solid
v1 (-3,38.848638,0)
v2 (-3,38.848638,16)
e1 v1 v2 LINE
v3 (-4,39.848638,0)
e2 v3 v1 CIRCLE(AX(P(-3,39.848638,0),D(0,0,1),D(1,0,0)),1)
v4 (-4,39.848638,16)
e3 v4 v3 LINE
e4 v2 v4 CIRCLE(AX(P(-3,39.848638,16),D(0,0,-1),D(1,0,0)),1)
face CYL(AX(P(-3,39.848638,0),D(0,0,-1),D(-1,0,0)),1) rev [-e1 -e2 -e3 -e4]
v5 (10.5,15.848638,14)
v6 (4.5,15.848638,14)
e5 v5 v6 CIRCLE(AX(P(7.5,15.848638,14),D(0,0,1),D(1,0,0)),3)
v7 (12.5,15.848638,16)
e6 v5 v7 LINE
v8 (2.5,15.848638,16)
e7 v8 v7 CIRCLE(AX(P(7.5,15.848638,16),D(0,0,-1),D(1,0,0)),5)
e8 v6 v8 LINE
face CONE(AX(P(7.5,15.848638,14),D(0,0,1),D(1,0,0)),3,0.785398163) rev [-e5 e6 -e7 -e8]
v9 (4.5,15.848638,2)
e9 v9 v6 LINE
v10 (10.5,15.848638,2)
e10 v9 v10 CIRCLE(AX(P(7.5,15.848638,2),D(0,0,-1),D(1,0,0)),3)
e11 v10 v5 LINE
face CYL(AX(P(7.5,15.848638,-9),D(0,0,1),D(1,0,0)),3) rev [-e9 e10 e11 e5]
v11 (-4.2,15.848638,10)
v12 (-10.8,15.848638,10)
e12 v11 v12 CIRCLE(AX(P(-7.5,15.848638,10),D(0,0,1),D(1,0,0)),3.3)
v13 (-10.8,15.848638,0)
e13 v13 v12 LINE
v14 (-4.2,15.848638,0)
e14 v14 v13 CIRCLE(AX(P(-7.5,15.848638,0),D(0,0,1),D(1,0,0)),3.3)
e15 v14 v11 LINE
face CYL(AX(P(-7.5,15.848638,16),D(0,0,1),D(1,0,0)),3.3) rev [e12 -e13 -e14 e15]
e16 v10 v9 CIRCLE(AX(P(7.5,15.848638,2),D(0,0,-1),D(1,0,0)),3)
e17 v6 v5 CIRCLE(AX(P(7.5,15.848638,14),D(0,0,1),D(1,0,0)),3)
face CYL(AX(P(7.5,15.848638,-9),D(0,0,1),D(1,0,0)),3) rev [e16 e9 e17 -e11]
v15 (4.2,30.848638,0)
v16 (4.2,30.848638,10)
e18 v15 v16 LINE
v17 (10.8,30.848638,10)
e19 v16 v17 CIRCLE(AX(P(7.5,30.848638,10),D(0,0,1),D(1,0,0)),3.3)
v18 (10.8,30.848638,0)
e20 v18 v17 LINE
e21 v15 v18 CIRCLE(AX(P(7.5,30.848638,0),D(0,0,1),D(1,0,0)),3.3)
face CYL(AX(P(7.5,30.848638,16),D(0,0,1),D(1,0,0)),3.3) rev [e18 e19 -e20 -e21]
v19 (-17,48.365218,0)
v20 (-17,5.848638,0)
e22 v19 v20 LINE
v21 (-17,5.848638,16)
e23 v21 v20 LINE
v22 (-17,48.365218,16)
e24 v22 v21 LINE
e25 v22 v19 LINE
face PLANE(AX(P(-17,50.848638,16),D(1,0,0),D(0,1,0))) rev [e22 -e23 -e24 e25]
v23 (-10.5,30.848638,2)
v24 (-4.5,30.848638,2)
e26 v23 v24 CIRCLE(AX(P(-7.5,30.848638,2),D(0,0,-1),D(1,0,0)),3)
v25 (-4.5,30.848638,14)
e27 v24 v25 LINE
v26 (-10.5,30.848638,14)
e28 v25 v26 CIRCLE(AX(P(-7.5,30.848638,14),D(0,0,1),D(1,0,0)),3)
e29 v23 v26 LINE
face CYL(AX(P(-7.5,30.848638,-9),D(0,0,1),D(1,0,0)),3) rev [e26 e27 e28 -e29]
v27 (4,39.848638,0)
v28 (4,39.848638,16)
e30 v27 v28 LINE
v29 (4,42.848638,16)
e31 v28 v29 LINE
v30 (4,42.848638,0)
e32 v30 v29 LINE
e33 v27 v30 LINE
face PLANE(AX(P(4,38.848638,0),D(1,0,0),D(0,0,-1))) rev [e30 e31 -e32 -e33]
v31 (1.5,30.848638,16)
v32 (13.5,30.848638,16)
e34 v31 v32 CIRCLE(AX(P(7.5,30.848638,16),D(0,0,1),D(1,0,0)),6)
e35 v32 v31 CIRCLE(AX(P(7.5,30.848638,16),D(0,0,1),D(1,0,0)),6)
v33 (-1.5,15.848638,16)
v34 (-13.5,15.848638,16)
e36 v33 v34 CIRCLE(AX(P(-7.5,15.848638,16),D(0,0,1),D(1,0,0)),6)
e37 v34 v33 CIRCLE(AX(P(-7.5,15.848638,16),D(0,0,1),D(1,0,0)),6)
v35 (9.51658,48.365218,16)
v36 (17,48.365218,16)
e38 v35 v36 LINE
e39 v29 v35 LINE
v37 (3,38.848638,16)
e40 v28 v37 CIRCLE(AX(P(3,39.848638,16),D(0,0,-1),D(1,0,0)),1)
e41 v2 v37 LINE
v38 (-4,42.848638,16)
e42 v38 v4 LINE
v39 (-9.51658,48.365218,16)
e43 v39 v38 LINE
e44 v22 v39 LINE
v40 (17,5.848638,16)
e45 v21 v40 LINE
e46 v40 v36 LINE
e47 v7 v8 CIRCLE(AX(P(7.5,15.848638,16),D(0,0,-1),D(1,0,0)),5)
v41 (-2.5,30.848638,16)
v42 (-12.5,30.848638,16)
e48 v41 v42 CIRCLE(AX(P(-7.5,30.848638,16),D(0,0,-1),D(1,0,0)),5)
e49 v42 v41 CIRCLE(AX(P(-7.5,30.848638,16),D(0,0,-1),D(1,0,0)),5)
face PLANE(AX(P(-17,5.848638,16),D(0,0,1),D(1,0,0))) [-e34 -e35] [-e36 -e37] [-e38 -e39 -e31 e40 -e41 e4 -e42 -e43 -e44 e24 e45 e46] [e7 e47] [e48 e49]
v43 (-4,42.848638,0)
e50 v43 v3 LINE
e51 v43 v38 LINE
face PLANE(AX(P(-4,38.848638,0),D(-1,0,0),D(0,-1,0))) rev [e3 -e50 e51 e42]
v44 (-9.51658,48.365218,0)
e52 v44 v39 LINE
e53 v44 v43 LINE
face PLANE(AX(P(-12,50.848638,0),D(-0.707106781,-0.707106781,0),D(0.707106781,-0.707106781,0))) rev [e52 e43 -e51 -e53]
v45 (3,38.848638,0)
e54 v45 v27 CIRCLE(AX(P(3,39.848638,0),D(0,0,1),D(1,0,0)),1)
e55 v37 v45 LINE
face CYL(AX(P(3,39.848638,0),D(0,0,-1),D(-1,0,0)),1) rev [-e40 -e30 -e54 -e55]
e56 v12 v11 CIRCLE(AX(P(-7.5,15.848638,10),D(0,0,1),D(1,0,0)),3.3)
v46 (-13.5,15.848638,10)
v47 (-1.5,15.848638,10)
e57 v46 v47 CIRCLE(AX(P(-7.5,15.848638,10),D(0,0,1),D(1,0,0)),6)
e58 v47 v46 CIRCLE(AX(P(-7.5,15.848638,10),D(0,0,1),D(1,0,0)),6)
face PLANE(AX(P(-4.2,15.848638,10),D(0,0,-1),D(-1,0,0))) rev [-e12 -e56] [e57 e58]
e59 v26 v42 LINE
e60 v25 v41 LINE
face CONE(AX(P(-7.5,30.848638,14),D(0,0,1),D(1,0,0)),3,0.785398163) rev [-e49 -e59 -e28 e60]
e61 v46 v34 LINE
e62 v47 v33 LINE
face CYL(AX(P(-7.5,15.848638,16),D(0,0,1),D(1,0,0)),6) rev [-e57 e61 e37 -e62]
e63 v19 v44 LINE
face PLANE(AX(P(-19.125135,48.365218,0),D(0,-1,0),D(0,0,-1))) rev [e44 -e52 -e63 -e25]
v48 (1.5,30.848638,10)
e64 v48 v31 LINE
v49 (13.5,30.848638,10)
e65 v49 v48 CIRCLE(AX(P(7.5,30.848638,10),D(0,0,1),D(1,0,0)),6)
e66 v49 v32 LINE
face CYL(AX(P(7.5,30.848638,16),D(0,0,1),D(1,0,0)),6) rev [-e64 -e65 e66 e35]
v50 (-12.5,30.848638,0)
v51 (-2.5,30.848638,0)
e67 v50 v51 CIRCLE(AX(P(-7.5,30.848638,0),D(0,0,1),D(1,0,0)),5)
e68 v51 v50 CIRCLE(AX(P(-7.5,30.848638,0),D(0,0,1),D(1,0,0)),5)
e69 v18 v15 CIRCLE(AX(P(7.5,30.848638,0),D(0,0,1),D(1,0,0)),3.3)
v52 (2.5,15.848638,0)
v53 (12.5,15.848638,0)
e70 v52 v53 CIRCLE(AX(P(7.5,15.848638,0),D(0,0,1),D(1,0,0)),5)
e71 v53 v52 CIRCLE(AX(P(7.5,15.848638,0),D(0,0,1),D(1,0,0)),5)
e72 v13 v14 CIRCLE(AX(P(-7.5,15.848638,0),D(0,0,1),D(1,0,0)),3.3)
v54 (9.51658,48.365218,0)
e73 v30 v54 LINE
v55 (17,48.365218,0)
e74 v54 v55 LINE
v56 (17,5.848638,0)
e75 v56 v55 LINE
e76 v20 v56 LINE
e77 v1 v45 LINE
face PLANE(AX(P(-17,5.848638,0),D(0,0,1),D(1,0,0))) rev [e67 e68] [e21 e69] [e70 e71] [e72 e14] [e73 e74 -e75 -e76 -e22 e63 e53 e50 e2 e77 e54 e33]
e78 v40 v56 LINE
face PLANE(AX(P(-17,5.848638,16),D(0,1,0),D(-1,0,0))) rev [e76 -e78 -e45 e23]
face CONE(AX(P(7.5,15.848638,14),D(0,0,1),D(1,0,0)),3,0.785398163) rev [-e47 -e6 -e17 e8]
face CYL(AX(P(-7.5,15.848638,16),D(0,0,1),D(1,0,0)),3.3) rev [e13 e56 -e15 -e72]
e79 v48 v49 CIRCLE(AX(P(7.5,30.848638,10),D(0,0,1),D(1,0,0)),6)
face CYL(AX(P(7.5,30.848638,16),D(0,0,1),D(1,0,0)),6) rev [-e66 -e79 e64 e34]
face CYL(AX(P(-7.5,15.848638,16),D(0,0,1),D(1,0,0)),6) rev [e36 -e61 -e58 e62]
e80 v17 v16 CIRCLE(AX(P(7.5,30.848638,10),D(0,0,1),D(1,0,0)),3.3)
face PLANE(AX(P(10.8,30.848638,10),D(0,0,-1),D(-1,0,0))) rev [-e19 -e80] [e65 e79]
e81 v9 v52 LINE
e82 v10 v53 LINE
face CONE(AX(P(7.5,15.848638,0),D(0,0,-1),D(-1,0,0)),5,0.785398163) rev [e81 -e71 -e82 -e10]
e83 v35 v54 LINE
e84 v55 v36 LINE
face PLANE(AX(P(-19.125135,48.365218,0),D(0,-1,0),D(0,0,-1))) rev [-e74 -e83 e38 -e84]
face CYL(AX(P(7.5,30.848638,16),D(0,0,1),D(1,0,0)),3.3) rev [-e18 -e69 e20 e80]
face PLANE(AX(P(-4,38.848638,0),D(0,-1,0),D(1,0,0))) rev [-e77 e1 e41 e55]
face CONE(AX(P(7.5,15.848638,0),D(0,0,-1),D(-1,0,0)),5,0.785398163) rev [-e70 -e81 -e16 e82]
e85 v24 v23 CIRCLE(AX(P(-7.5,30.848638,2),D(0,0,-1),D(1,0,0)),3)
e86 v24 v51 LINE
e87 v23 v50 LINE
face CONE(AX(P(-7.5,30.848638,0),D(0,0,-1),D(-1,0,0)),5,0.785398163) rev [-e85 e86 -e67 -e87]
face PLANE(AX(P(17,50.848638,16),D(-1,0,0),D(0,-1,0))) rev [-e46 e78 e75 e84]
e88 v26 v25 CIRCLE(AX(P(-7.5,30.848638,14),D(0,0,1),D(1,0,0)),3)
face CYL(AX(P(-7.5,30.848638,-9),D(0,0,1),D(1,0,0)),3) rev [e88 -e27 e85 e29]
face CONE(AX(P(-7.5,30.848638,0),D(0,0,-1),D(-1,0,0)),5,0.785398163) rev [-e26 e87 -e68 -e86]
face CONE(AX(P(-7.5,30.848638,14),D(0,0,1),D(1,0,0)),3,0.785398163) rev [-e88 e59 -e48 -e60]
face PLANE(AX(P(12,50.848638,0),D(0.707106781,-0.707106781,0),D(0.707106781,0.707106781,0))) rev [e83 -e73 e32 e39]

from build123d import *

# Parameters (mm, degrees)
SKETCH1_W                                = 34
SKETCH1_H                                = 45
BASE_EXTRUDE_DEPTH                       = 16
CUT_EXTRUDE1_DEPTH                       = 56.951622292
CBORE_FOR_M5_HEX_HEAD_SCREW1_D           = 6.6
CBORE_FOR_M5_HEX_HEAD_SCREW1_CBORE_D     = 12
CBORE_FOR_M5_HEX_HEAD_SCREW1_CBORE_DEPTH = 6
SKETCH3_R                                = 3
CUT_EXTRUDE4_DEPTH                       = 25
CHAMFER3_SIZE                            = 2
CHAMFER4_SIZE                            = 2
CBORE_FOR_M5_HEX_HEAD_SCREW2_D           = 6.6
CBORE_FOR_M5_HEX_HEAD_SCREW2_CBORE_D     = 12
CBORE_FOR_M5_HEX_HEAD_SCREW2_CBORE_DEPTH = 6
FILLET1_R                                = 1
FILLET2_R                                = 1
SKETCH13_W                               = 37.795873191
SKETCH13_H                               = 5.669380978
CUT_EXTRUDE5_DEPTH                       = 56.951622292


with BuildPart() as part:
    # Sketch1 → Base-Extrude (new body)
    with BuildSketch(Plane.XY):
        with Locations((0, 28.348638498)):
            Rectangle(SKETCH1_W, SKETCH1_H)
    extrude(amount=BASE_EXTRUDE_DEPTH)

    # Sketch2 → Cut-Extrude1 (cut, through all)
    with BuildSketch(Plane.XY.offset(16)):
        Polygon((-4, 38.848638498), (4, 38.848638498), (4, 42.848638498), (12, 50.848638498), (-12, 50.848638498), (-4, 42.848638498), align=None)
    extrude(amount=-CUT_EXTRUDE1_DEPTH, mode=Mode.SUBTRACT)

    # CBORE for M5 Hex Head Screw1 (through all)
    with Locations(Plane.XY.offset(16)):
        with Locations((7.5, 30.848638498)):
            CounterBoreHole(CBORE_FOR_M5_HEX_HEAD_SCREW1_D / 2, CBORE_FOR_M5_HEX_HEAD_SCREW1_CBORE_D / 2, CBORE_FOR_M5_HEX_HEAD_SCREW1_CBORE_DEPTH)

    # Sketch3 → Cut-Extrude4 (cut)
    with BuildSketch(Plane.XY.offset(16)):
        with Locations((-7.5, 30.848638498)):
            Circle(SKETCH3_R)
        with Locations((7.5, 15.848638498)):
            Circle(SKETCH3_R)
    extrude(amount=-CUT_EXTRUDE4_DEPTH, mode=Mode.SUBTRACT)

    # Chamfer3
    chamfer3_edges = [part.edges().sort_by_distance(p)[0] for p in [
        (-10.5, 30.848638498, 16),
        (4.5, 15.848638498, 16),
    ]]
    chamfer(chamfer3_edges, length=CHAMFER3_SIZE)

    # Chamfer4
    chamfer4_edges = [part.edges().sort_by_distance(p)[0] for p in [
        (-10.5, 30.848638498, 0),
        (4.5, 15.848638498, 0),
    ]]
    chamfer(chamfer4_edges, length=CHAMFER4_SIZE)

    # CBORE for M5 Hex Head Screw2 (through all)
    with Locations(Plane.XY.offset(16)):
        with Locations((-7.5, 15.848638498)):
            CounterBoreHole(CBORE_FOR_M5_HEX_HEAD_SCREW2_D / 2, CBORE_FOR_M5_HEX_HEAD_SCREW2_CBORE_D / 2, CBORE_FOR_M5_HEX_HEAD_SCREW2_CBORE_DEPTH)

    # Fillet1
    fillet1_edges = [part.edges().sort_by_distance(p)[0] for p in [
        (-4, 38.848638498, 8),
    ]]
    fillet(fillet1_edges, radius=FILLET1_R)

    # Fillet2
    fillet2_edges = [part.edges().sort_by_distance(p)[0] for p in [
        (4, 38.848638498, 8),
    ]]
    fillet(fillet2_edges, radius=FILLET2_R)

    # Sketch13 → Cut-Extrude5 (cut, through all)
    with BuildSketch(Plane.XY.offset(16)):
        with Locations((-0.227198085, 51.199908502)):
            Rectangle(SKETCH13_W, SKETCH13_H)
    extrude(amount=-CUT_EXTRUDE5_DEPTH, mode=Mode.SUBTRACT)


solid = part.part
